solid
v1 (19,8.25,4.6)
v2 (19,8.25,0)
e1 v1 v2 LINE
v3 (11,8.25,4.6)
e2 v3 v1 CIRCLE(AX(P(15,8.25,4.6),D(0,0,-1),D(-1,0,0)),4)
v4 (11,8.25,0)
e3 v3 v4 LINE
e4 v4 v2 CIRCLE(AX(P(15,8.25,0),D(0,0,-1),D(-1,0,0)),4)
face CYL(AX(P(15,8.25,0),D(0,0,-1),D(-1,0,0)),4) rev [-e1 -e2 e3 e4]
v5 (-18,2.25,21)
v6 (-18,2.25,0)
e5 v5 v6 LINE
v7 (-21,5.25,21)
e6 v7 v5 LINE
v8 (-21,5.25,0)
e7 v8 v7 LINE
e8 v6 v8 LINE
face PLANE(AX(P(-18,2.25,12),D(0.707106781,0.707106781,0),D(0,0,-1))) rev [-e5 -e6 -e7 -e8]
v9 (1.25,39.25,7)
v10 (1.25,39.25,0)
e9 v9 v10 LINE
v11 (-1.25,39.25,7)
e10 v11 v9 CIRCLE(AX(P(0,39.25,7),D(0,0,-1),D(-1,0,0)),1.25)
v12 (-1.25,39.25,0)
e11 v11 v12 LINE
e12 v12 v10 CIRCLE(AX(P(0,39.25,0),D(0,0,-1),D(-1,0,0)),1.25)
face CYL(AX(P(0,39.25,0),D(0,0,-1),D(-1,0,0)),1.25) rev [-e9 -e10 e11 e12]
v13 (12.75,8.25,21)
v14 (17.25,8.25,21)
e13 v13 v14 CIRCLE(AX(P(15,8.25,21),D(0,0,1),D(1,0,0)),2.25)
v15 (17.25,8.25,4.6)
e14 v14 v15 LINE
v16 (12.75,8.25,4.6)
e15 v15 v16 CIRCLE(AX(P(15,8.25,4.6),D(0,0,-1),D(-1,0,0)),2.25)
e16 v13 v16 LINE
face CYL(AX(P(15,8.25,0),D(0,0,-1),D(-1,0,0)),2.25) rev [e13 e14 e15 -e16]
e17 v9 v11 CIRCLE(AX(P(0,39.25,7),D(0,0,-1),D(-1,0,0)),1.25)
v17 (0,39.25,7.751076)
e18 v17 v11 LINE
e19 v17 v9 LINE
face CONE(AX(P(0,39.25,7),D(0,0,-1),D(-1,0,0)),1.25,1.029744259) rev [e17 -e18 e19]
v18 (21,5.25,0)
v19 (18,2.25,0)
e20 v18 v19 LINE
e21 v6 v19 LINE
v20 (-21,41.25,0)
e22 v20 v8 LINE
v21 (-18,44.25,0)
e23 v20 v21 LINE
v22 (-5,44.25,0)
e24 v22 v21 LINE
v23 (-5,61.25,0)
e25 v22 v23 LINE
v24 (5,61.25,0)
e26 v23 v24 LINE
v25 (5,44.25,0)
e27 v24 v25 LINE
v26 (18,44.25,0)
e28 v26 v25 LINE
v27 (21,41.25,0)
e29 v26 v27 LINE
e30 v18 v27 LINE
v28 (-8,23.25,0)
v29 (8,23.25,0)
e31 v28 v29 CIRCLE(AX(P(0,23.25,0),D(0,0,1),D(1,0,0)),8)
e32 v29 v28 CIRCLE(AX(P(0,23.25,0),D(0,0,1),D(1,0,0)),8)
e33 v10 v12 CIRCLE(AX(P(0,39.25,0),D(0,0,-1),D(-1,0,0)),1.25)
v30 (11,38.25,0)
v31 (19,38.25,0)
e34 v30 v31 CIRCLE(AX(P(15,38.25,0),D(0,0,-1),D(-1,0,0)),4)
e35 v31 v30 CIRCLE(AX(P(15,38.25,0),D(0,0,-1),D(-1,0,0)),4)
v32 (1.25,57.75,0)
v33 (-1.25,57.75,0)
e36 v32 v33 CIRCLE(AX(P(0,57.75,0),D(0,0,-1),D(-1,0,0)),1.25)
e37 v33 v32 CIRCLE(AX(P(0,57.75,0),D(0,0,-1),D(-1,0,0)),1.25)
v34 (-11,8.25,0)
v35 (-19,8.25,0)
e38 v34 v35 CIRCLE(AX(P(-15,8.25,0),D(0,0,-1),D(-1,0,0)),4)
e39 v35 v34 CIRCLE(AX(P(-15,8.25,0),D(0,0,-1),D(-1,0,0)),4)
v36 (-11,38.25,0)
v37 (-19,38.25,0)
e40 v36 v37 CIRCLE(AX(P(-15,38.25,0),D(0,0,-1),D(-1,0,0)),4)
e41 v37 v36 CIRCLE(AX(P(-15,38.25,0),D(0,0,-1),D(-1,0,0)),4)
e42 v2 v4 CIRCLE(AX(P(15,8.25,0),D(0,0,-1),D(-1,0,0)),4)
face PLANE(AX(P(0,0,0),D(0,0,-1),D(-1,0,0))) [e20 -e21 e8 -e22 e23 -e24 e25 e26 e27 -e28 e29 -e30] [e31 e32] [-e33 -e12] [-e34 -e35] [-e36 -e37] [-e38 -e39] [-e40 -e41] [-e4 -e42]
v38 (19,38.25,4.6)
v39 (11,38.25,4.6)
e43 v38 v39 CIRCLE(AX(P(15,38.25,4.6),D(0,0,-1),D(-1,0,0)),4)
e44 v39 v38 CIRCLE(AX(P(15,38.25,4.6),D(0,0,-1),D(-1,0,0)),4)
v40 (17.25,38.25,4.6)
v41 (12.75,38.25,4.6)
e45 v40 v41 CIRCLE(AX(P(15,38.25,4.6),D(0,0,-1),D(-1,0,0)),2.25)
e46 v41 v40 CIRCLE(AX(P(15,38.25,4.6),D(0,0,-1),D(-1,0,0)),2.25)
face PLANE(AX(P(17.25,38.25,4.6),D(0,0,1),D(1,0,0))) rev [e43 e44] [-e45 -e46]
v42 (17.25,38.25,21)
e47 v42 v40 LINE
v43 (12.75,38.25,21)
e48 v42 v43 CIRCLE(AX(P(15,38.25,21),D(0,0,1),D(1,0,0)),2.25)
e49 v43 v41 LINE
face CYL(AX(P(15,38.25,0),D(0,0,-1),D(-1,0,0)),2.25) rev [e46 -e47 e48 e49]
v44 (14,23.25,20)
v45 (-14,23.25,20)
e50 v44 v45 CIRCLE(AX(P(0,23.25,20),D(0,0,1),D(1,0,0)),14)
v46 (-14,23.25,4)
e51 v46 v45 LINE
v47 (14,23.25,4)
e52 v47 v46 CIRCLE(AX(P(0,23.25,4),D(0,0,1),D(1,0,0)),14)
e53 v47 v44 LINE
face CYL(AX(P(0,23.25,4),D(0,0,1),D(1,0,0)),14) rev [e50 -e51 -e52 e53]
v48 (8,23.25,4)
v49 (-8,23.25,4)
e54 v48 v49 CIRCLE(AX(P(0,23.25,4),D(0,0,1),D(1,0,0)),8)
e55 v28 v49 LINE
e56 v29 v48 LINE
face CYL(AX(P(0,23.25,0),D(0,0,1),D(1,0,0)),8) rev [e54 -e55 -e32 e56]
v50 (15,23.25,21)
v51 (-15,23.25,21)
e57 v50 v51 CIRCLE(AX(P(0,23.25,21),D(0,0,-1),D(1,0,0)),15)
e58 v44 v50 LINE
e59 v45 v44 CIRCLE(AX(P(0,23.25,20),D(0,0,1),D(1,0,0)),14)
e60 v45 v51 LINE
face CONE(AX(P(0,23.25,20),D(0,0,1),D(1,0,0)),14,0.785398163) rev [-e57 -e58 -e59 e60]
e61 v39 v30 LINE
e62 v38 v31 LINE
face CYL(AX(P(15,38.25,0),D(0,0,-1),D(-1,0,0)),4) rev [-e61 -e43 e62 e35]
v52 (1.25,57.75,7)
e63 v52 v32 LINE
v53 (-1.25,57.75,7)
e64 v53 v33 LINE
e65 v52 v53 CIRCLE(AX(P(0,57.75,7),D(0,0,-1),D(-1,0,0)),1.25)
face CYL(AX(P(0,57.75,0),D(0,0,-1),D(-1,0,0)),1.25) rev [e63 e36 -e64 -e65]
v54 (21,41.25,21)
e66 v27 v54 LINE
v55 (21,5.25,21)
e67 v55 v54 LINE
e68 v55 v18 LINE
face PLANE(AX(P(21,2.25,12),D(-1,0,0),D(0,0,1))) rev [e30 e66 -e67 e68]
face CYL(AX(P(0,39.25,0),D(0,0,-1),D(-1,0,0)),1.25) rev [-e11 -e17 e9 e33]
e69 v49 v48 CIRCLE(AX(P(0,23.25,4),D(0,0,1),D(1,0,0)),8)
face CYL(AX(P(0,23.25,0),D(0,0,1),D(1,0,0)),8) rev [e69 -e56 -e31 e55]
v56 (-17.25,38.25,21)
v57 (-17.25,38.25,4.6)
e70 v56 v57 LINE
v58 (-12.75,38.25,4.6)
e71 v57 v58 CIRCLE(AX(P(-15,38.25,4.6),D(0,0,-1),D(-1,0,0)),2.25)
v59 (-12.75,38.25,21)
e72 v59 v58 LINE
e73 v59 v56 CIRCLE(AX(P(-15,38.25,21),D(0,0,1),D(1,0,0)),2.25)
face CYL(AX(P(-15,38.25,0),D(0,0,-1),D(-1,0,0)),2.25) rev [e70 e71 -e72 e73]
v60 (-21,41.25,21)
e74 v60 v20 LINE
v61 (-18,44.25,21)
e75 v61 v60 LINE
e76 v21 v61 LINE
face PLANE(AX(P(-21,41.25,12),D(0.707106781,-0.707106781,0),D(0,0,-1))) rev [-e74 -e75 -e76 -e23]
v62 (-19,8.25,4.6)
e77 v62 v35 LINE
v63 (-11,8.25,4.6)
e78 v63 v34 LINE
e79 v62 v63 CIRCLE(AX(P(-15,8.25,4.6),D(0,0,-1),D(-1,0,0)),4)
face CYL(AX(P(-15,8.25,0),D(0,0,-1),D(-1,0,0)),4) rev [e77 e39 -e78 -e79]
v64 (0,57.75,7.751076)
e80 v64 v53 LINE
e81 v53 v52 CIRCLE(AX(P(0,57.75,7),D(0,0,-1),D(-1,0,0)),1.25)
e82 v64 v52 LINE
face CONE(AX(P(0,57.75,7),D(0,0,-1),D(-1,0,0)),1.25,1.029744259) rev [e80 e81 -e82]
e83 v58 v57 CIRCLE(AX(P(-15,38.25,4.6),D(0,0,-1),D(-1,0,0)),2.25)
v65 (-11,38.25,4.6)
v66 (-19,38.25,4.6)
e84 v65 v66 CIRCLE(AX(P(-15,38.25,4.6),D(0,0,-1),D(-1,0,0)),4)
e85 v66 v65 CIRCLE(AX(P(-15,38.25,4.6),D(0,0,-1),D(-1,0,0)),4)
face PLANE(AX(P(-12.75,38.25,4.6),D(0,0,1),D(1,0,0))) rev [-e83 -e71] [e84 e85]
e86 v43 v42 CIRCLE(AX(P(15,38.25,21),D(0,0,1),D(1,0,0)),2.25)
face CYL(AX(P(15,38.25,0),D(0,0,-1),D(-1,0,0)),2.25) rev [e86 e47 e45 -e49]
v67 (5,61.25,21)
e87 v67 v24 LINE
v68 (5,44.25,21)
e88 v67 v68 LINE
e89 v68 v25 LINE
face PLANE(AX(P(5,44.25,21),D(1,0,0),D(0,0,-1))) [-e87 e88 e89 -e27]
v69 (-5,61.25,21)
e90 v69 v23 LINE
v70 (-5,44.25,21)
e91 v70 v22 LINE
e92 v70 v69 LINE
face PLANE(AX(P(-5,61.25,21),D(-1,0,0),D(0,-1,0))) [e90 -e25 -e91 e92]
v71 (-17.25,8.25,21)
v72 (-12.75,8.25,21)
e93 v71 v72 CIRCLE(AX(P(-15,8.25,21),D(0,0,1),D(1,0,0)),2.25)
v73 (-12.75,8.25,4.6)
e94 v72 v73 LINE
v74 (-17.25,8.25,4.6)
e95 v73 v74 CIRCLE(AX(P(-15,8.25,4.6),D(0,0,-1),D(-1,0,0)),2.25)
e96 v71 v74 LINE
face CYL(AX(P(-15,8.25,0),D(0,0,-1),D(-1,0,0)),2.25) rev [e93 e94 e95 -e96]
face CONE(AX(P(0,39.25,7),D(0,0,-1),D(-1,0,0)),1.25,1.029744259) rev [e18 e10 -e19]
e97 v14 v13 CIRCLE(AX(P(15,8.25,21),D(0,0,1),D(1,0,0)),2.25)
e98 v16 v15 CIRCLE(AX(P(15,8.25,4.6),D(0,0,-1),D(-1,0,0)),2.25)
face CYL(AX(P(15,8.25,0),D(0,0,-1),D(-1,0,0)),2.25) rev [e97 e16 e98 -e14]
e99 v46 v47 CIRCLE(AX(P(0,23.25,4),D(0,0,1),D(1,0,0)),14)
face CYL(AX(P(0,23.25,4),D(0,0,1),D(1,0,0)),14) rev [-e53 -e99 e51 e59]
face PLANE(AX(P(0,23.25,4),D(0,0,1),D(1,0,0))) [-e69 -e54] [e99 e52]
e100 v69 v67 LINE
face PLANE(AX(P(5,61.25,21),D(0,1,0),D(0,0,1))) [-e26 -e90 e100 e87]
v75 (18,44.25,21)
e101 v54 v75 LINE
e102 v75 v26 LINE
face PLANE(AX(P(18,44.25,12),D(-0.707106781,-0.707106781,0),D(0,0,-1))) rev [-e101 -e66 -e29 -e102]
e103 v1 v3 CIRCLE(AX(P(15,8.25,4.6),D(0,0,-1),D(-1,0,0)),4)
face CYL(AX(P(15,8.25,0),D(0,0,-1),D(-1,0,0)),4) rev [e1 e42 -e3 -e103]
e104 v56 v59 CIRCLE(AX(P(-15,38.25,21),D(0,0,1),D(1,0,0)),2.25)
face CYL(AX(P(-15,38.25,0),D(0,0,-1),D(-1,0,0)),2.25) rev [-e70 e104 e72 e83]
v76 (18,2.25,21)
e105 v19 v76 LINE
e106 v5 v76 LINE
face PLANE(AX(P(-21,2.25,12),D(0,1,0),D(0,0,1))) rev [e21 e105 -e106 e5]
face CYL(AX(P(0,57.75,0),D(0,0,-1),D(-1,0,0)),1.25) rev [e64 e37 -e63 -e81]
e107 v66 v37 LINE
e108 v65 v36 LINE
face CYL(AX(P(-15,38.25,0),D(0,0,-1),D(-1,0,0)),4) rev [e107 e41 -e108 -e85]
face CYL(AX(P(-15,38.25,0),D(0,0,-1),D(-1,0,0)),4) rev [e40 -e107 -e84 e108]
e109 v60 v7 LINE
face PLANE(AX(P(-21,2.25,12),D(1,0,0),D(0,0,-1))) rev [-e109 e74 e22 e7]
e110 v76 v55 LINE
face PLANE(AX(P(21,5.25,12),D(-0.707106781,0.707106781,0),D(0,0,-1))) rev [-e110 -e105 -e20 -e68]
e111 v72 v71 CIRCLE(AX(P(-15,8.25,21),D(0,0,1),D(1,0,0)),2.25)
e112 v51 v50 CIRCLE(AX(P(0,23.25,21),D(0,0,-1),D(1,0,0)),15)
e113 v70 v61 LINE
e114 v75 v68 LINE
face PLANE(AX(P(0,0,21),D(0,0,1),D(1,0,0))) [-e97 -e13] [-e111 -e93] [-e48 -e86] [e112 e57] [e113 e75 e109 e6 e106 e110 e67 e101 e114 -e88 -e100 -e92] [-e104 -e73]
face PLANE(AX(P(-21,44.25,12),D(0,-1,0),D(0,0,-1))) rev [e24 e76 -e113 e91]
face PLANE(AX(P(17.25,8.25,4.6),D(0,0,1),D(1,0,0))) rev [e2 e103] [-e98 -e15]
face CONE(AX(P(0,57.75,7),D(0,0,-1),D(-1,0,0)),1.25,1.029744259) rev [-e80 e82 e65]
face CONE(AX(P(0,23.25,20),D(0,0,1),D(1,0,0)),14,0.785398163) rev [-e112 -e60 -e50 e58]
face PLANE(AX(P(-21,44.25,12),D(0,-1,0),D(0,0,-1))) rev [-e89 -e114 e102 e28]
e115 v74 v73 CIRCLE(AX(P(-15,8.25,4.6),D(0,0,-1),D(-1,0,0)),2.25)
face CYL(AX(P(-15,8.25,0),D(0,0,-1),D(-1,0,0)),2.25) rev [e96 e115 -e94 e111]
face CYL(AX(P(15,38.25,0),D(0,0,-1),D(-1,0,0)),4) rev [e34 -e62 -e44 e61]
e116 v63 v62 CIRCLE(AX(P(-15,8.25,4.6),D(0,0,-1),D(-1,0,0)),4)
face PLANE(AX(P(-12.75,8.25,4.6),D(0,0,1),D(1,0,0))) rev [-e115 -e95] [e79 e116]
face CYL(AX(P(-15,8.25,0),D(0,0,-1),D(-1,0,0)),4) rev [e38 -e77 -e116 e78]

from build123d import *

# Parameters (mm, degrees)
SKETCH_1_W                = 42
SKETCH_1_H                = 42
EXTRUDE_1_DEPTH           = 12
SKETCH_2_R                = 14
CUT_EXTRUDE_1_DEPTH       = 8
SKETCH_3_R                = 8
CUT_EXTRUDE_2_DEPTH       = 50.629250448
CHAMFER_1_SIZE            = 3
HOLE_WIZARD_2_D           = 4.5
HOLE_WIZARD_2_CBORE_D     = 8
HOLE_WIZARD_2_CBORE_DEPTH = 4.6
EXTRUDE_START             = 9
SKETCH_10_R               = 2.25
SKETCH_10_R_2             = 14
EXTRUDE_2_DEPTH           = 9
SKETCH_11_W               = 10
SKETCH_11_H               = 17
EXTRUDE_3_DEPTH           = 21
HOLE_WIZARD_M3_1_D        = 2.5
HOLE_WIZARD_M3_1_DEPTH    = 7
HOLE_WIZARD_M3_1_TIP      = 0.751075774
CHAMFER_2_SIZE            = 1


with BuildPart() as part:
    # 草图1 → 凸台-拉伸1 (new body)
    with BuildSketch(Plane.XY):
        with Locations((0, 23.25)):
            Rectangle(SKETCH_1_W, SKETCH_1_H)
    extrude(amount=EXTRUDE_1_DEPTH)

    # 草图2 → 切除-拉伸1 (cut)
    with BuildSketch(Plane.XY.offset(12)):
        with Locations((0, 23.25)):
            Circle(SKETCH_2_R)
    extrude(amount=-CUT_EXTRUDE_1_DEPTH, mode=Mode.SUBTRACT)

    # 草图3 → 切除-拉伸2 (cut, through all)
    with BuildSketch(Plane.XY.offset(4)):
        with Locations((0, 23.25)):
            Circle(SKETCH_3_R)
    extrude(amount=-CUT_EXTRUDE_2_DEPTH, mode=Mode.SUBTRACT)

    # 倒角1
    chamfer_1_edges = [part.edges().sort_by_distance(p)[0] for p in [
        (21, 2.25, 6),
        (-21, 2.25, 6),
        (-21, 44.25, 6),
        (21, 44.25, 6),
    ]]
    chamfer(chamfer_1_edges, length=CHAMFER_1_SIZE)

    # 打孔尺寸根据内六角圆柱头螺钉的类型2 (through all)
    with Locations(Plane(origin=(0, 0, 0), x_dir=(-1, 0, 0), z_dir=(0, 0, -1))):
        with Locations((-15, 38.25), (15, 38.25), (15, 8.25), (-15, 8.25)):
            CounterBoreHole(HOLE_WIZARD_2_D / 2, HOLE_WIZARD_2_CBORE_D / 2, HOLE_WIZARD_2_CBORE_DEPTH)

    # 草图10 → 凸台-拉伸2 (add)
    with BuildSketch(Plane.XY.offset(12).offset(EXTRUDE_START)):
        Polygon((-18, 2.25), (18, 2.25), (21, 5.25), (21, 41.25), (18, 44.25), (-18, 44.25), (-21, 41.25), (-21, 5.25), align=None)
        with Locations(Location((-15, 38.25, 0), (0, 0, 180))):
            Circle(SKETCH_10_R, mode=Mode.SUBTRACT)
        with Locations((0, 23.25)):
            Circle(SKETCH_10_R_2, mode=Mode.SUBTRACT)
        with Locations(Location((15, 38.25, 0), (0, 0, 180))):
            Circle(SKETCH_10_R, mode=Mode.SUBTRACT)
        with Locations(Location((15, 8.25, 0), (0, 0, 180))):
            Circle(SKETCH_10_R, mode=Mode.SUBTRACT)
        with Locations(Location((-15, 8.25, 0), (0, 0, 180))):
            Circle(SKETCH_10_R, mode=Mode.SUBTRACT)
    extrude(amount=-EXTRUDE_2_DEPTH)

    # 草图11 → 凸台-拉伸3 (add)
    with BuildSketch(Plane(origin=(0, 0, 0), x_dir=(-1, 0, 0), z_dir=(0, 0, -1))):
        with Locations((0, 52.75)):
            Rectangle(SKETCH_11_W, SKETCH_11_H)
    extrude(amount=-EXTRUDE_3_DEPTH)

    # M3 螺纹孔1
    with Locations(Plane(origin=(0, 0, 0), x_dir=(-1, 0, 0), z_dir=(0, 0, -1))):
        with Locations((0, 57.75), (0, 39.25)):
            Hole(HOLE_WIZARD_M3_1_D / 2, depth=HOLE_WIZARD_M3_1_DEPTH)
            with Locations((0, 0, -(HOLE_WIZARD_M3_1_DEPTH + HOLE_WIZARD_M3_1_TIP / 2))):  # 118° drill point
                Cone(0, HOLE_WIZARD_M3_1_D / 2, HOLE_WIZARD_M3_1_TIP, mode=Mode.SUBTRACT)

    # 倒角2
    chamfer_2_edges = [part.edges().sort_by_distance(p)[0] for p in [
        (-14, 23.25, 21),
    ]]
    chamfer(chamfer_2_edges, length=CHAMFER_2_SIZE)


solid = part.part
